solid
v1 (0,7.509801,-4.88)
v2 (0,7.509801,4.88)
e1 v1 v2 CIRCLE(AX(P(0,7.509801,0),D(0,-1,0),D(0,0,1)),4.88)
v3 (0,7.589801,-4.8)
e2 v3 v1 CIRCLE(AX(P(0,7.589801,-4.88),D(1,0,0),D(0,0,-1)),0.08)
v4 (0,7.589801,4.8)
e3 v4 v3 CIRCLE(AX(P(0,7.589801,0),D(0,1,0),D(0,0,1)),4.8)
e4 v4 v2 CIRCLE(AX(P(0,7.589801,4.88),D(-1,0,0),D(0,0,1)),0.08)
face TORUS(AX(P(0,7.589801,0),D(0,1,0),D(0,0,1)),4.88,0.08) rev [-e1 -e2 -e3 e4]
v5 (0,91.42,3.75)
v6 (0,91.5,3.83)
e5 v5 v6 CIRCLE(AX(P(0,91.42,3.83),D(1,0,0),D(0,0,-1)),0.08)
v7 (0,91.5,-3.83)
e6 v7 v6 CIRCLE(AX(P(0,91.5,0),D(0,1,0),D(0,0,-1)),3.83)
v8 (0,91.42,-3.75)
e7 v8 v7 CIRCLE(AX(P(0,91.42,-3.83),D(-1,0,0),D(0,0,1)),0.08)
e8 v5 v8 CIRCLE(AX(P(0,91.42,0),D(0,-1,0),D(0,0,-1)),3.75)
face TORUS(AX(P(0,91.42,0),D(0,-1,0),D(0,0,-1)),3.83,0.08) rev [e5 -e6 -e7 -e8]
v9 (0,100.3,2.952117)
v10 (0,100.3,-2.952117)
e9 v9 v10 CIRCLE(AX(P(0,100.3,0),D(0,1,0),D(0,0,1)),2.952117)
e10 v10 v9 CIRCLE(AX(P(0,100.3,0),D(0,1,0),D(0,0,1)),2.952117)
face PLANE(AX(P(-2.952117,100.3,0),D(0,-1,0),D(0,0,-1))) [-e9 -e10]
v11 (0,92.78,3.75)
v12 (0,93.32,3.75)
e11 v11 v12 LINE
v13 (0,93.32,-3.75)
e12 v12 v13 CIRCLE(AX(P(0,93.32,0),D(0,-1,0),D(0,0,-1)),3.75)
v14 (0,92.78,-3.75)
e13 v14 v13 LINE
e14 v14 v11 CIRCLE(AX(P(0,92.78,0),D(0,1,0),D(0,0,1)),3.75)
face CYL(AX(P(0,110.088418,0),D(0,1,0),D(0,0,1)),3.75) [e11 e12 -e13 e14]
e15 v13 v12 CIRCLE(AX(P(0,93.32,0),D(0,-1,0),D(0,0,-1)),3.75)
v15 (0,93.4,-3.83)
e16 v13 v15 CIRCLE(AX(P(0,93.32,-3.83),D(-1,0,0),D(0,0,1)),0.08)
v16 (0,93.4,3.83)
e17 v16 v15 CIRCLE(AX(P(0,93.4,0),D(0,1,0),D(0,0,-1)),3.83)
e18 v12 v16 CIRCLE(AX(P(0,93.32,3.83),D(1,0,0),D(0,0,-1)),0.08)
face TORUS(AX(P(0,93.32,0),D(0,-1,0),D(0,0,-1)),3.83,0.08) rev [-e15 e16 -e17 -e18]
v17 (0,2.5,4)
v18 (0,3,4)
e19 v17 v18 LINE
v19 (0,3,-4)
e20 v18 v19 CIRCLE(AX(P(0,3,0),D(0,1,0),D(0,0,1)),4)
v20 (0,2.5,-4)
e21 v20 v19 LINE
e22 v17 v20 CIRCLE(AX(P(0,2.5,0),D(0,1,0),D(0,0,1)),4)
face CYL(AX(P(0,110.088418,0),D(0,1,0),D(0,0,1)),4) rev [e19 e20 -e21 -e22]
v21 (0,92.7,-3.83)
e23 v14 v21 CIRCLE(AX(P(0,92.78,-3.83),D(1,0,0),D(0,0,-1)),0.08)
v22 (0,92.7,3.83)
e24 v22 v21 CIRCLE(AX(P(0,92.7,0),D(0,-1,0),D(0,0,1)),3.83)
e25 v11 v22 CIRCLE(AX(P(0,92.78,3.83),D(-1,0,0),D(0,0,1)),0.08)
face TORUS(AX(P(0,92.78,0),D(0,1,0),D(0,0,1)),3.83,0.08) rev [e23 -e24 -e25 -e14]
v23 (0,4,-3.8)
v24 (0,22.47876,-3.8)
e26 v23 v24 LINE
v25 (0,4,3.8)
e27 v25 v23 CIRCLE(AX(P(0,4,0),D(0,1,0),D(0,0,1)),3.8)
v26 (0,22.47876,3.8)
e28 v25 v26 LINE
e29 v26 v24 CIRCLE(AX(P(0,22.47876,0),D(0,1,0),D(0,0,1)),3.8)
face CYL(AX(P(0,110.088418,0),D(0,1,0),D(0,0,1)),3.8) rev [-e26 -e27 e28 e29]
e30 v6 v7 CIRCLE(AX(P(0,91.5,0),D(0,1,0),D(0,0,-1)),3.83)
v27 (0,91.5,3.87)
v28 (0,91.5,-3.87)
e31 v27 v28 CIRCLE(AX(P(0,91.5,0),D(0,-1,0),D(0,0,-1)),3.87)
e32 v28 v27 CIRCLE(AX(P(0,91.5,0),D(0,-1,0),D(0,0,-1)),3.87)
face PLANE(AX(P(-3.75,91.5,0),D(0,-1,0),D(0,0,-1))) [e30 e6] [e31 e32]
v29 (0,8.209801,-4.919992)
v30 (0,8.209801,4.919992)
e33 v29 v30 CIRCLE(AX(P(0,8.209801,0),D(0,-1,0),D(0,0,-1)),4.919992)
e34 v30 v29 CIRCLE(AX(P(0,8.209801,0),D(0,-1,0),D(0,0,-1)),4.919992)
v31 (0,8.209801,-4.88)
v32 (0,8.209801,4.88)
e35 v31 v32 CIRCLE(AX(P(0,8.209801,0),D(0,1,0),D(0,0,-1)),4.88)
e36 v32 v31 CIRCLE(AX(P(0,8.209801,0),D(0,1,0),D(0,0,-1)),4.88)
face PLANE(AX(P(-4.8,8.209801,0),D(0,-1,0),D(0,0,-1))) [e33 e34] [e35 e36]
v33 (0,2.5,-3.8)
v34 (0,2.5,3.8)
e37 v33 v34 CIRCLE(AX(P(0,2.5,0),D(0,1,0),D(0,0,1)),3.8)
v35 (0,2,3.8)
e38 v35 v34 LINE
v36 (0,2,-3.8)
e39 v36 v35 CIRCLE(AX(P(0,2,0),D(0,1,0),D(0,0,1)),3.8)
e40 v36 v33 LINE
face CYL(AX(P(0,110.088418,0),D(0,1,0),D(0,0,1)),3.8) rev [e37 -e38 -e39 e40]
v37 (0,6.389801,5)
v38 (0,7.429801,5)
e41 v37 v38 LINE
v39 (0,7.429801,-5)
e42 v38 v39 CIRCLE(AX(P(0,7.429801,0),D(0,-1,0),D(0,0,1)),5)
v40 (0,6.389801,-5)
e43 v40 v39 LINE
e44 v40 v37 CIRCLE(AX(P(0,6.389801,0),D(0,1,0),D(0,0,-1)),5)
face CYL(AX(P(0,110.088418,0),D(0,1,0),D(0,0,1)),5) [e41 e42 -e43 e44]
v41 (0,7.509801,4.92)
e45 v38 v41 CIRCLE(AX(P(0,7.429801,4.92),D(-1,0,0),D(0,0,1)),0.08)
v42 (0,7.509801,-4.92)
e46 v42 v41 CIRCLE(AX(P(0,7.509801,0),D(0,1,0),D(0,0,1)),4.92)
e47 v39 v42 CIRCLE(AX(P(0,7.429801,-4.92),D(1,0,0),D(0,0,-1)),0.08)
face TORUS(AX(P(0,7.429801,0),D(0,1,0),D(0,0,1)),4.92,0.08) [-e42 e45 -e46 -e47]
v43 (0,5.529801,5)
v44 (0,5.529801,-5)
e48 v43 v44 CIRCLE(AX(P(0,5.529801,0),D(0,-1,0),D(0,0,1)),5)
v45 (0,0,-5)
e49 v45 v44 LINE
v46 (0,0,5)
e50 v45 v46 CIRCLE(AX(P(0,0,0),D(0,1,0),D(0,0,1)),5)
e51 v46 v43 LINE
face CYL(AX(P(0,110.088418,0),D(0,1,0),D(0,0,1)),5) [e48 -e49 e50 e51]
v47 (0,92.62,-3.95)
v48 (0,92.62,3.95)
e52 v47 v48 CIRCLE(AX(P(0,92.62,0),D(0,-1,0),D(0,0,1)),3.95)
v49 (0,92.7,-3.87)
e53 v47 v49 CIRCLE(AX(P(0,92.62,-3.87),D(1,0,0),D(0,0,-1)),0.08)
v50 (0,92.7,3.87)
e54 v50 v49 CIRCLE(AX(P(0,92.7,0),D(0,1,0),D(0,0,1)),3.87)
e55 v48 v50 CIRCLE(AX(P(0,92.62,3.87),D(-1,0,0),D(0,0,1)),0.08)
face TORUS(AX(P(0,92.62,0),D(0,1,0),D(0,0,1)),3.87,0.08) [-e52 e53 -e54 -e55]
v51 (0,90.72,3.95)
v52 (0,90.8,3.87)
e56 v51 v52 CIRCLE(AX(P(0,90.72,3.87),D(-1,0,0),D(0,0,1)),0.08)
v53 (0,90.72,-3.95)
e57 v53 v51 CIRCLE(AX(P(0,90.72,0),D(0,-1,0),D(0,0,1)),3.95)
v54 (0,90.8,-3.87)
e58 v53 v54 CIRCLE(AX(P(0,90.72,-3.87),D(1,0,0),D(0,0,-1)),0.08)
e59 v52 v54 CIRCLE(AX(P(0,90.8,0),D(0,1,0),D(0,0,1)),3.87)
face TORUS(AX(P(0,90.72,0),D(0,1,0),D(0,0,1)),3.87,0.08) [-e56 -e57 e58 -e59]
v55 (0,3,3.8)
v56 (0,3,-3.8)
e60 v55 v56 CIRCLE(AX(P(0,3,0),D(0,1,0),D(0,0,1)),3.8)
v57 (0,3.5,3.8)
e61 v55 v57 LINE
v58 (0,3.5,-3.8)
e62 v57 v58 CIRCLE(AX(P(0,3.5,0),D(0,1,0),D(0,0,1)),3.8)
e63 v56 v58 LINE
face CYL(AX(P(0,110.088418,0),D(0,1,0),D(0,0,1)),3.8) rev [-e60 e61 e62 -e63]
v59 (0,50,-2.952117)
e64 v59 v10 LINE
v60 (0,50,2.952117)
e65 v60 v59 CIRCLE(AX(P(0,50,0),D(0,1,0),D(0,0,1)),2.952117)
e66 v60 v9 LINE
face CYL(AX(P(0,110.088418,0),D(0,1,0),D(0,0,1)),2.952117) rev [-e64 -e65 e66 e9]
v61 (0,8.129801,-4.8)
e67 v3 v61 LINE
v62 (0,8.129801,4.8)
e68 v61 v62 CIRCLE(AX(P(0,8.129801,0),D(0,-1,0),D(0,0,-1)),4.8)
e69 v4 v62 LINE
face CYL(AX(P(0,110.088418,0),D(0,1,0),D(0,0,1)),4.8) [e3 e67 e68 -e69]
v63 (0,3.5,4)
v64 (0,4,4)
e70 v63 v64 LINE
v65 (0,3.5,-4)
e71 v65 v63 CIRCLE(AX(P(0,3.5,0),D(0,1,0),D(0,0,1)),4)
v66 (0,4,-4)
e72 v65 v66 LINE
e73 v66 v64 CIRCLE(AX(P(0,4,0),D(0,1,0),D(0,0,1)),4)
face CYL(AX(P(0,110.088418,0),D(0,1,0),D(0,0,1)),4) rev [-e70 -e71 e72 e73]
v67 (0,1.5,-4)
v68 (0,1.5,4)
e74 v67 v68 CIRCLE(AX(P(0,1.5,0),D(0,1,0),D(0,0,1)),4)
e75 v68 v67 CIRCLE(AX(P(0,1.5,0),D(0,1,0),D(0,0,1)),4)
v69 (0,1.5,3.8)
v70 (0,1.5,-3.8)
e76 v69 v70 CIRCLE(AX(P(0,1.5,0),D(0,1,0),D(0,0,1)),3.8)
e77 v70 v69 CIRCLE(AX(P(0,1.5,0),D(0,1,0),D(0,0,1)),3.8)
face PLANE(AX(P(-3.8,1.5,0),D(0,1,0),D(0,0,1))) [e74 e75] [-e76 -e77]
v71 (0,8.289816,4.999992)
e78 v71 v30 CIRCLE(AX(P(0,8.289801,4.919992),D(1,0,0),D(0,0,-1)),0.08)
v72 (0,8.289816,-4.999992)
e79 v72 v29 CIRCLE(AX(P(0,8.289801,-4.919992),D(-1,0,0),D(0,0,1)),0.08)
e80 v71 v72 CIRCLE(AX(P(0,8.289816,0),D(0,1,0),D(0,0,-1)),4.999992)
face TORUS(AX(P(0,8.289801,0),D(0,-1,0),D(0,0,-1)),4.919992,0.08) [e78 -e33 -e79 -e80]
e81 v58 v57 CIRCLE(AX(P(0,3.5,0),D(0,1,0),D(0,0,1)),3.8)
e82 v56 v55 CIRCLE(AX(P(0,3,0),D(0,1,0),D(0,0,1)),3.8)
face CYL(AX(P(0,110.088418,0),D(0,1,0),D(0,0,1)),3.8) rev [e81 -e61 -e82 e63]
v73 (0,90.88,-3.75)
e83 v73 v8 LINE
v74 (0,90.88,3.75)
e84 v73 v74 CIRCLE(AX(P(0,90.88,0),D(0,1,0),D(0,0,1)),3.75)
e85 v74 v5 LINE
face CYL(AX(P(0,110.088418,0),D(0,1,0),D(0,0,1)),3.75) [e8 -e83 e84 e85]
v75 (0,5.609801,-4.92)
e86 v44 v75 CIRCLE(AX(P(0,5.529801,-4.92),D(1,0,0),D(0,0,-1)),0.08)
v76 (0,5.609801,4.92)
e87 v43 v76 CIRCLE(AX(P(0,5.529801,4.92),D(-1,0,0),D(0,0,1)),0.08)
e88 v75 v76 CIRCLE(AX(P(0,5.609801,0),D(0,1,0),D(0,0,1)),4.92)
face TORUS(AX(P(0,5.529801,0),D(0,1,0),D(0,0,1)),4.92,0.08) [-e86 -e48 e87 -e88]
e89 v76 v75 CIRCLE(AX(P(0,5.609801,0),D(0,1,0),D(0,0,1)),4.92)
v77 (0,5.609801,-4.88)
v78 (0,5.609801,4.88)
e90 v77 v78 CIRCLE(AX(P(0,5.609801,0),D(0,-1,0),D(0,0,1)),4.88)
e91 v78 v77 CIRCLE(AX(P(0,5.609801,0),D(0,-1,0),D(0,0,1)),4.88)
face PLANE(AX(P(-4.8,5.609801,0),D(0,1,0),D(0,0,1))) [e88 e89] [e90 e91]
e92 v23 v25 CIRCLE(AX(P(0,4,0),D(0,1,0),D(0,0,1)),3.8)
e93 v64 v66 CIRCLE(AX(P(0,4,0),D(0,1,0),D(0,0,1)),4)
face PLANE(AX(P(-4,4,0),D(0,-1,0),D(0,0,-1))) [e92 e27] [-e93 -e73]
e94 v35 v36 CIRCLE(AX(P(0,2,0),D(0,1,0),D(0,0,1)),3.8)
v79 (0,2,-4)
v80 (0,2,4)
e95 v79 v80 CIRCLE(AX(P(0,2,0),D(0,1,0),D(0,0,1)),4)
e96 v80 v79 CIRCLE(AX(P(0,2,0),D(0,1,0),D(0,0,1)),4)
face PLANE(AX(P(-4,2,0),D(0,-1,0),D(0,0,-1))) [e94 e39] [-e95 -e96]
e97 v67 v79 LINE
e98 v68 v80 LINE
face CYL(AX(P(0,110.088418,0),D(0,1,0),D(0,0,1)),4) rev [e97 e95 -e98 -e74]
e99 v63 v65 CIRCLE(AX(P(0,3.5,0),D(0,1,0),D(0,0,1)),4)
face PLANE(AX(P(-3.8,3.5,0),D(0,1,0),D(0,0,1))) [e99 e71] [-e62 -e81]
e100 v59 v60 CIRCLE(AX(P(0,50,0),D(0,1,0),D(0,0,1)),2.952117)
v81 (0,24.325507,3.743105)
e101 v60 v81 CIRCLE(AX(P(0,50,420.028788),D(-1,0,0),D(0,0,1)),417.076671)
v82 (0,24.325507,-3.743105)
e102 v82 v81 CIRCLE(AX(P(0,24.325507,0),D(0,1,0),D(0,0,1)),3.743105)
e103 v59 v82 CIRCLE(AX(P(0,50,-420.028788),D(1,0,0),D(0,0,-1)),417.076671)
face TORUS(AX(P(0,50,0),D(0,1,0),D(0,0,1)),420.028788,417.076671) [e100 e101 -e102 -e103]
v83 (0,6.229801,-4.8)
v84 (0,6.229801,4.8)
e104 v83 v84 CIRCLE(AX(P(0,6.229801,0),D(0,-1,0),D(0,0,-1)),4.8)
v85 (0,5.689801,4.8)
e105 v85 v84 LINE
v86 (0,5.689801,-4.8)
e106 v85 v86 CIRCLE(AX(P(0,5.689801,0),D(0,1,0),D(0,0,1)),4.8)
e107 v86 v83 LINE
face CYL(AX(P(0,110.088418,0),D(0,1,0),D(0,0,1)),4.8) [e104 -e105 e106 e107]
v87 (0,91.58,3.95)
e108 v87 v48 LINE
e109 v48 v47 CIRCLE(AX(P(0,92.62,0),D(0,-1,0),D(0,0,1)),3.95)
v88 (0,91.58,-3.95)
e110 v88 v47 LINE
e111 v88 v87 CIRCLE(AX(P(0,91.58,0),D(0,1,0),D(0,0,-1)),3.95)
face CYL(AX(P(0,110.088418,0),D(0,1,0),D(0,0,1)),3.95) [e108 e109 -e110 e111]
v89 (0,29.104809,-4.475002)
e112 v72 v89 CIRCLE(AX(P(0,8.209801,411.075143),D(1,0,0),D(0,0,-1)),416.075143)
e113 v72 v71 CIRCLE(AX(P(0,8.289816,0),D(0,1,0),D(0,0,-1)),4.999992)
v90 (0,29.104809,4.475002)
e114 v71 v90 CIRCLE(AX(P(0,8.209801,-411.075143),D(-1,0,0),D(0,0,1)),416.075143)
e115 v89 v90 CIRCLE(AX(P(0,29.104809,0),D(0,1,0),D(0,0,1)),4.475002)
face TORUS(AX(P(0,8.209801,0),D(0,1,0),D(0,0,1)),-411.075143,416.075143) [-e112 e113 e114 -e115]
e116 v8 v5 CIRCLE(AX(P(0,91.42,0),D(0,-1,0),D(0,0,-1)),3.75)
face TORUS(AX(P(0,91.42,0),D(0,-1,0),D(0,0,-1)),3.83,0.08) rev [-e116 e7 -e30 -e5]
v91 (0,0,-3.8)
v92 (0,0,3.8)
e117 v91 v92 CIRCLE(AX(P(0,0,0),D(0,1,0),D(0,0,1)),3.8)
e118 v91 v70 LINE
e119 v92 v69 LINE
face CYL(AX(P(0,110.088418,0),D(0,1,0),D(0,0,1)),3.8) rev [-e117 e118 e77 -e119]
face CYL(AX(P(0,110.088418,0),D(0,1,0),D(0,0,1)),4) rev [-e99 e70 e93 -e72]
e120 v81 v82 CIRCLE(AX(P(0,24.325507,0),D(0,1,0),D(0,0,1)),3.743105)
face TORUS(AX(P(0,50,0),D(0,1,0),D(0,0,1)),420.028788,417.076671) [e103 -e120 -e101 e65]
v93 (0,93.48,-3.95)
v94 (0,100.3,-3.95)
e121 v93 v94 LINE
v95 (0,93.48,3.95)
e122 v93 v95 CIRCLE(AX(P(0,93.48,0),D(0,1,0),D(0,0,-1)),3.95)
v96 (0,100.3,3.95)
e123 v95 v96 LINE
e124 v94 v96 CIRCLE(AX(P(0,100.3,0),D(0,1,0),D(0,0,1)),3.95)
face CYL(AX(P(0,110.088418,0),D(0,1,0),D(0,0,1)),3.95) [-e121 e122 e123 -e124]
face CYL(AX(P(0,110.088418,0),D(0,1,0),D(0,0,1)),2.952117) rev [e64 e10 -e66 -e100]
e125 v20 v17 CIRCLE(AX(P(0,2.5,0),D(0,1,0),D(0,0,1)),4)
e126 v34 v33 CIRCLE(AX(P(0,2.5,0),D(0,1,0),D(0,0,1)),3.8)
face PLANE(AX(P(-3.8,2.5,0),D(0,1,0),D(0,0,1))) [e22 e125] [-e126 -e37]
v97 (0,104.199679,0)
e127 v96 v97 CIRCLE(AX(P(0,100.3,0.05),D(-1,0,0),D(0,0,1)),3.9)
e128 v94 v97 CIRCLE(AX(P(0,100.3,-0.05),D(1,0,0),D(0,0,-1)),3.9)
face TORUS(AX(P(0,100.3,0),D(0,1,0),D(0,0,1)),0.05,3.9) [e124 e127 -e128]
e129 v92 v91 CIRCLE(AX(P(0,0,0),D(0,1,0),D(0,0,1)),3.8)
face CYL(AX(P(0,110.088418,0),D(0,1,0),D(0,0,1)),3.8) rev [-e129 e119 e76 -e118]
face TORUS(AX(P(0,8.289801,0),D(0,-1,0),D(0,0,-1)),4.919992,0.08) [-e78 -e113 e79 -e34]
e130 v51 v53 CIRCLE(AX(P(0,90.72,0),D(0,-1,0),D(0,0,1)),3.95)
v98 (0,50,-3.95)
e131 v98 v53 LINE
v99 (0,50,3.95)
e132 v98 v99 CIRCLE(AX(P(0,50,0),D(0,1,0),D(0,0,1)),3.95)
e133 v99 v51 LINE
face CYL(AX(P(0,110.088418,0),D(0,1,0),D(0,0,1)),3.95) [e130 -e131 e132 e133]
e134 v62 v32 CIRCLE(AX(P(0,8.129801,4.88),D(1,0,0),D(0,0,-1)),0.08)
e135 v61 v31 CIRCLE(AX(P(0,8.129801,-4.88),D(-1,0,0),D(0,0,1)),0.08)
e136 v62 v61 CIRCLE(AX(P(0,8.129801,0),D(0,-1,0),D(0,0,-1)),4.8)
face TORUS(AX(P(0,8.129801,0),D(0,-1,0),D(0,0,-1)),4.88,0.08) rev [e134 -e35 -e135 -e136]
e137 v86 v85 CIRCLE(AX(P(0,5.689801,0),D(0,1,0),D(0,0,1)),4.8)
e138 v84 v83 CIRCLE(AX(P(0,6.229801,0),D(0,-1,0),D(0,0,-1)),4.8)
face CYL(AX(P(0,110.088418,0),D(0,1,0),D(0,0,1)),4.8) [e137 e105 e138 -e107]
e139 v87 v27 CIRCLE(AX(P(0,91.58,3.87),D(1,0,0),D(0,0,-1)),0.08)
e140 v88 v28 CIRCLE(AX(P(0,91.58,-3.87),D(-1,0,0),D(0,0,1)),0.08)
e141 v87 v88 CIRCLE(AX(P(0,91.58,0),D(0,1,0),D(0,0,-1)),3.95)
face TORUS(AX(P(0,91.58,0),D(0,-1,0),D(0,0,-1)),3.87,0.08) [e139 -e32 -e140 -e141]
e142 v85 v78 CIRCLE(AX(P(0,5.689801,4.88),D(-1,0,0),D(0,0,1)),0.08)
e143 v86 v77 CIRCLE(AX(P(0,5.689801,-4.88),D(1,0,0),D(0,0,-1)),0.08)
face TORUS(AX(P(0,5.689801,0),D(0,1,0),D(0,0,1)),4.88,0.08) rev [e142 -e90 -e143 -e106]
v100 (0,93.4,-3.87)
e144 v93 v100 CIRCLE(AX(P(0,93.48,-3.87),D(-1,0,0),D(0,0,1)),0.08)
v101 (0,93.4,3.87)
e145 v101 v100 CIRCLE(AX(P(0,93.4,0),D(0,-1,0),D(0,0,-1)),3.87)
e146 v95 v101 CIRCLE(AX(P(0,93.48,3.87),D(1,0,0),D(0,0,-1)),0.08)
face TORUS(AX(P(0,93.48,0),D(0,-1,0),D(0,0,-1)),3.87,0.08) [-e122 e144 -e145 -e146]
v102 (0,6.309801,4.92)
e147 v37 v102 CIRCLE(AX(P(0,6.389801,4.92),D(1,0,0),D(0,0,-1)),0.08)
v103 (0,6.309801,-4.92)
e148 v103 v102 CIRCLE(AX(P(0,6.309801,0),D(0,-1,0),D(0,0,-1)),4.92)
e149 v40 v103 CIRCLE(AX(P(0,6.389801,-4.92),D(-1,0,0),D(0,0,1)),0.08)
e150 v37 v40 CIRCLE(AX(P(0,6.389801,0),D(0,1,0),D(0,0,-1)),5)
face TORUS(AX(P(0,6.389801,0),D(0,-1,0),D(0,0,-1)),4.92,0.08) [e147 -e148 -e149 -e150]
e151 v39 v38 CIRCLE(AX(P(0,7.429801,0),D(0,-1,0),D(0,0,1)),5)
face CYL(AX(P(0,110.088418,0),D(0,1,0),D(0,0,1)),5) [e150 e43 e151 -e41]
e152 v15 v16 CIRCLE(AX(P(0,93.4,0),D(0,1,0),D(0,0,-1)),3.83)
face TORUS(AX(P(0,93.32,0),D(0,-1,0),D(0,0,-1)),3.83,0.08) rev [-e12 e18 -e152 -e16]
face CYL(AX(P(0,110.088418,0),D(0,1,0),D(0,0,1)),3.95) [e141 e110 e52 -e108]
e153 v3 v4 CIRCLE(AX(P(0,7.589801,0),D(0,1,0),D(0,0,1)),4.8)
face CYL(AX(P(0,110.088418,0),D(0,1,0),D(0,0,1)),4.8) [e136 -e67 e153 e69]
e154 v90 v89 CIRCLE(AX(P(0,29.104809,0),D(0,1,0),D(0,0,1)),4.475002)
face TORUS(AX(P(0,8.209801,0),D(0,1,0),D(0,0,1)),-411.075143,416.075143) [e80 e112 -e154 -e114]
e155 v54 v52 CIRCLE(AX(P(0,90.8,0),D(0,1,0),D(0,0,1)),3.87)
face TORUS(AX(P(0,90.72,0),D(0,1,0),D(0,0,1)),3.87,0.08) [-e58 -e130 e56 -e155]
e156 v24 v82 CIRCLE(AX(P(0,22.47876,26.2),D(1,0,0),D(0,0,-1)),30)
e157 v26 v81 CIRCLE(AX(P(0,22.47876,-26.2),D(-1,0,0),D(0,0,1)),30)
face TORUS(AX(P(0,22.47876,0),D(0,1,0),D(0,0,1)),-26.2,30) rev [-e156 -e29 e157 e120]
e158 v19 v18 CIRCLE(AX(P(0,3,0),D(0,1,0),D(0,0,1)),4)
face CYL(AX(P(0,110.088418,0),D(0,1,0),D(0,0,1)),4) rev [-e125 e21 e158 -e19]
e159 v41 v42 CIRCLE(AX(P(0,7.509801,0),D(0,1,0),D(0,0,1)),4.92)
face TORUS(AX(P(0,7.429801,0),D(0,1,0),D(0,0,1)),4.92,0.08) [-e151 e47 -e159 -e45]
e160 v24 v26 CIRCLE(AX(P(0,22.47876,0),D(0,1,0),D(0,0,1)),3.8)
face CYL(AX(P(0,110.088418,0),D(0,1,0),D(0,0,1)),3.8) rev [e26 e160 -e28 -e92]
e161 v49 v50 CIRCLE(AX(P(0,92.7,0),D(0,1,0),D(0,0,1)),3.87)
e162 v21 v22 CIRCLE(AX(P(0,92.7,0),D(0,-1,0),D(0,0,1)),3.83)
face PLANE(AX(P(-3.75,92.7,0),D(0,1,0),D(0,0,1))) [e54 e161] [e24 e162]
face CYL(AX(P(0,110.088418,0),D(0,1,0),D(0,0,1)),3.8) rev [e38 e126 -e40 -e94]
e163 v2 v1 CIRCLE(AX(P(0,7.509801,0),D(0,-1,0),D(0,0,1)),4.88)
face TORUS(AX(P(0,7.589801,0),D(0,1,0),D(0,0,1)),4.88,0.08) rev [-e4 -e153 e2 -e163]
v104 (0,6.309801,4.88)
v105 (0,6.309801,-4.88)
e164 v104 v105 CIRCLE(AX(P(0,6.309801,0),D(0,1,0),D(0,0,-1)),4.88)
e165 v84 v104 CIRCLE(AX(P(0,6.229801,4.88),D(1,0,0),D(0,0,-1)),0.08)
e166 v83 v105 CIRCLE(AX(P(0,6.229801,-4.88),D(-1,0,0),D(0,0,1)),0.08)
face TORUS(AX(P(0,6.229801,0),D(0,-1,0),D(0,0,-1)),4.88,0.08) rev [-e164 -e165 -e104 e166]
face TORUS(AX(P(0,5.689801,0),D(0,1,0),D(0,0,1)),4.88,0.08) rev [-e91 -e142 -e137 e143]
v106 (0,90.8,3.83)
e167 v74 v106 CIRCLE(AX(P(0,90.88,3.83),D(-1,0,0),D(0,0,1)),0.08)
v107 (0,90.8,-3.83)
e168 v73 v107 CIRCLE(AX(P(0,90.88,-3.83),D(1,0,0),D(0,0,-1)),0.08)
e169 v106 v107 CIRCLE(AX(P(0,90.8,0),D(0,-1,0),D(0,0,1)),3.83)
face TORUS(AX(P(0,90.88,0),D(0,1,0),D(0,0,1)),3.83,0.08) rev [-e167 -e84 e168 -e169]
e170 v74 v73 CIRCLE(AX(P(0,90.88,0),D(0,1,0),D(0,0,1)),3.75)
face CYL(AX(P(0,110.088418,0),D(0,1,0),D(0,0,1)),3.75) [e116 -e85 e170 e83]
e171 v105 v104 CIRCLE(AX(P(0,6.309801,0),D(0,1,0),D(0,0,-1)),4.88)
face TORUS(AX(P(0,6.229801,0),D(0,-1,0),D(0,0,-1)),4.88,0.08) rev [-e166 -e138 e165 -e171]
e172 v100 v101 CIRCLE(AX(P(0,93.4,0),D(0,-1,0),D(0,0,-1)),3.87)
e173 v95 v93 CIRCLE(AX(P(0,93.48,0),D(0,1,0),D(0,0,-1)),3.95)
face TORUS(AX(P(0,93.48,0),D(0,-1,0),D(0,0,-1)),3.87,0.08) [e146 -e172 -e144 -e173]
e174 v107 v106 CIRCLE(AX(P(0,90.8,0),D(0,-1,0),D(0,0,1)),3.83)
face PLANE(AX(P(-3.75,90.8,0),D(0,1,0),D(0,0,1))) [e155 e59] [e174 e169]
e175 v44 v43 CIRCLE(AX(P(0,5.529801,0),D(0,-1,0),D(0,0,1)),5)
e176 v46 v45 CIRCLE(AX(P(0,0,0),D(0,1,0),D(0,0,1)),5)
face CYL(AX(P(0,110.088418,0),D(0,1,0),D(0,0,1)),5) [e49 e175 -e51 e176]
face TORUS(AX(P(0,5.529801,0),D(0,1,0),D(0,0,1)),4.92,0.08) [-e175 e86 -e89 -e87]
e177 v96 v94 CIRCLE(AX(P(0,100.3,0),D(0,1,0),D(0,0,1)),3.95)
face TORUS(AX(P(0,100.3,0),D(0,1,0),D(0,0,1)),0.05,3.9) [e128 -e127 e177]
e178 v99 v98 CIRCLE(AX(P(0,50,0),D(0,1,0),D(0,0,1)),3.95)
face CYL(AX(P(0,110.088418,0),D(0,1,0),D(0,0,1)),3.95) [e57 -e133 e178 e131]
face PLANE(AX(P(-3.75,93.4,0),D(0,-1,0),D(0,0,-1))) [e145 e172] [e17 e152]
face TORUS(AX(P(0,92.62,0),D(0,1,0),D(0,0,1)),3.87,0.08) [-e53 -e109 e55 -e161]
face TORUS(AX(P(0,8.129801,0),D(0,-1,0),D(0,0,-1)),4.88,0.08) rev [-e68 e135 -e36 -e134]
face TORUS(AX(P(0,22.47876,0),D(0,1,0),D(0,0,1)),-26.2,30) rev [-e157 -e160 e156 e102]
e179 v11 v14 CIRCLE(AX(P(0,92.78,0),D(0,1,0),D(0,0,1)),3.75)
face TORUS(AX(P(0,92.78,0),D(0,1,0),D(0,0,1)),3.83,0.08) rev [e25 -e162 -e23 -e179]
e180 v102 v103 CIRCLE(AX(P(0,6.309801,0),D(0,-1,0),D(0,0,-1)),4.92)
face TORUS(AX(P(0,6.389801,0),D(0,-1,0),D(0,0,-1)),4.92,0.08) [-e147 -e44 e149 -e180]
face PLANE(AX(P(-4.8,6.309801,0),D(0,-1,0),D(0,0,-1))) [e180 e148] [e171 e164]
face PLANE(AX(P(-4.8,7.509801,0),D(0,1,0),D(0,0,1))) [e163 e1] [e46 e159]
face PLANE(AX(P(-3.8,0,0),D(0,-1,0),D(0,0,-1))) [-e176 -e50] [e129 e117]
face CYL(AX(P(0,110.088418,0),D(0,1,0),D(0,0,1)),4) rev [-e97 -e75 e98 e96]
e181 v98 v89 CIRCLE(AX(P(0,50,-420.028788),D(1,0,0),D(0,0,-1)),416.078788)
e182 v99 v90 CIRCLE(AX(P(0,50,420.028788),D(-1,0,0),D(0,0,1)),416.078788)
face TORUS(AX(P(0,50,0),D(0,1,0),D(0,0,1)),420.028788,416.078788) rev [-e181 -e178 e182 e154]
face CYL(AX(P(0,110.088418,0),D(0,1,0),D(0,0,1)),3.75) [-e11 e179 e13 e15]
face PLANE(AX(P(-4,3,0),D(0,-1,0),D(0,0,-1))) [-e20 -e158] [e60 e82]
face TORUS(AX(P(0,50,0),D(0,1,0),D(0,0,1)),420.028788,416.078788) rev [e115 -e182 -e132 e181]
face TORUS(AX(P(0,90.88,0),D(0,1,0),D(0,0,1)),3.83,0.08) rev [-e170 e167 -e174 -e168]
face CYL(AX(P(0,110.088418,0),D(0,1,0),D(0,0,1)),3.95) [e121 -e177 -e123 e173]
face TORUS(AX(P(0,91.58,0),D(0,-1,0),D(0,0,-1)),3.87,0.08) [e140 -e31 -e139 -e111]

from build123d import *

# Parameters (mm, degrees)
FILLET1_R = 0.08


with BuildPart() as part:
    # Sketch2 → Revolve1 (revolve)
    with BuildSketch(Plane.XY, mode=Mode.PRIVATE) as revolve1_sk:
        with BuildLine():
            Line((-5, 0), (-5, 5.609800729))
            Line((-5, 5.609800729), (-4.8, 5.609800729))
            Line((-4.8, 5.609800729), (-4.8, 6.309800729))
            Line((-4.8, 6.309800729), (-5, 6.309800729))
            Line((-5, 6.309800729), (-5, 7.509800729))
            Line((-5, 7.509800729), (-4.8, 7.509800729))
            Line((-4.8, 7.509800729), (-4.8, 8.209800729))
            Line((-4.8, 8.209800729), (-5, 8.209800729))
            ThreePointArc((-5, 8.209800729), (-4.868729867, 18.660601983), (-4.475002299, 29.104808861))
            ThreePointArc((-4.475002299, 29.104808861), (-4.081271283, 39.549107214), (-3.95, 50))
            Line((-3.95, 50), (-3.95, 90.8))
            Line((-3.95, 90.8), (-3.75, 90.8))
            Line((-3.75, 90.8), (-3.75, 91.5))
            Line((-3.75, 91.5), (-3.95, 91.5))
            Line((-3.95, 91.5), (-3.95, 92.7))
            Line((-3.95, 92.7), (-3.75, 92.7))
            Line((-3.75, 92.7), (-3.75, 93.4))
            Line((-3.75, 93.4), (-3.95, 93.4))
            Line((-3.95, 93.4), (-3.95, 100.3))
            ThreePointArc((-3.95, 100.3), (-2.789981752, 103.075337817), (0, 104.199679474))
            Line((0, 104.199679474), (0, 100.3))
            Line((0, 100.3), (-2.95211686, 100.3))
            Line((-2.95211686, 100.3), (-2.95211686, 50))
            ThreePointArc((-2.95211686, 50), (-3.149910758, 37.156662475), (-3.74310485, 24.325506566))
            ThreePointArc((-3.74310485, 24.325506566), (-3.785772839, 23.402571518), (-3.8, 22.478760255))
            Line((-3.8, 22.478760255), (-3.8, 4))
            Line((-3.8, 4), (-4, 4))
            Line((-4, 4), (-4, 3.5))
            Line((-4, 3.5), (-3.8, 3.5))
            Line((-3.8, 3.5), (-3.8, 3))
            Line((-3.8, 3), (-4, 3))
            Line((-4, 3), (-4, 2.5))
            Line((-4, 2.5), (-3.8, 2.5))
            Line((-3.8, 2.5), (-3.8, 2))
            Line((-3.8, 2), (-4, 2))
            Line((-4, 2), (-4, 1.5))
            Line((-4, 1.5), (-3.8, 1.5))
            Line((-3.8, 1.5), (-3.8, 0))
            Line((-3.8, 0), (-5, 0))
        make_face()
    revolve(revolve1_sk.sketch.rotate(Axis((0, 110.08841758, 0), (0, -1, 0)), 270), axis=Axis((0, 110.08841758, 0), (0, -1, 0)))

    # Fillet1
    fillet1_edges = [part.edges().sort_by_distance(p)[0] for p in [
        (0, 5.609800729, -5),
        (0, 5.609800729, -4.8),
        (0, 6.309800729, -4.8),
        (0, 6.309800729, -5),
        (0, 7.509800729, -5),
        (0, 7.509800729, -4.8),
        (0, 8.209800729, -4.8),
        (0, 8.209800729, -5),
        (0, 90.8, -3.95),
        (0, 90.8, -3.75),
        (0, 91.5, -3.75),
        (0, 91.5, -3.95),
        (0, 92.7, -3.95),
        (0, 92.7, -3.75),
        (0, 93.4, -3.75),
        (0, 93.4, -3.95),
    ]]
    fillet(fillet1_edges, radius=FILLET1_R)


solid = part.part
